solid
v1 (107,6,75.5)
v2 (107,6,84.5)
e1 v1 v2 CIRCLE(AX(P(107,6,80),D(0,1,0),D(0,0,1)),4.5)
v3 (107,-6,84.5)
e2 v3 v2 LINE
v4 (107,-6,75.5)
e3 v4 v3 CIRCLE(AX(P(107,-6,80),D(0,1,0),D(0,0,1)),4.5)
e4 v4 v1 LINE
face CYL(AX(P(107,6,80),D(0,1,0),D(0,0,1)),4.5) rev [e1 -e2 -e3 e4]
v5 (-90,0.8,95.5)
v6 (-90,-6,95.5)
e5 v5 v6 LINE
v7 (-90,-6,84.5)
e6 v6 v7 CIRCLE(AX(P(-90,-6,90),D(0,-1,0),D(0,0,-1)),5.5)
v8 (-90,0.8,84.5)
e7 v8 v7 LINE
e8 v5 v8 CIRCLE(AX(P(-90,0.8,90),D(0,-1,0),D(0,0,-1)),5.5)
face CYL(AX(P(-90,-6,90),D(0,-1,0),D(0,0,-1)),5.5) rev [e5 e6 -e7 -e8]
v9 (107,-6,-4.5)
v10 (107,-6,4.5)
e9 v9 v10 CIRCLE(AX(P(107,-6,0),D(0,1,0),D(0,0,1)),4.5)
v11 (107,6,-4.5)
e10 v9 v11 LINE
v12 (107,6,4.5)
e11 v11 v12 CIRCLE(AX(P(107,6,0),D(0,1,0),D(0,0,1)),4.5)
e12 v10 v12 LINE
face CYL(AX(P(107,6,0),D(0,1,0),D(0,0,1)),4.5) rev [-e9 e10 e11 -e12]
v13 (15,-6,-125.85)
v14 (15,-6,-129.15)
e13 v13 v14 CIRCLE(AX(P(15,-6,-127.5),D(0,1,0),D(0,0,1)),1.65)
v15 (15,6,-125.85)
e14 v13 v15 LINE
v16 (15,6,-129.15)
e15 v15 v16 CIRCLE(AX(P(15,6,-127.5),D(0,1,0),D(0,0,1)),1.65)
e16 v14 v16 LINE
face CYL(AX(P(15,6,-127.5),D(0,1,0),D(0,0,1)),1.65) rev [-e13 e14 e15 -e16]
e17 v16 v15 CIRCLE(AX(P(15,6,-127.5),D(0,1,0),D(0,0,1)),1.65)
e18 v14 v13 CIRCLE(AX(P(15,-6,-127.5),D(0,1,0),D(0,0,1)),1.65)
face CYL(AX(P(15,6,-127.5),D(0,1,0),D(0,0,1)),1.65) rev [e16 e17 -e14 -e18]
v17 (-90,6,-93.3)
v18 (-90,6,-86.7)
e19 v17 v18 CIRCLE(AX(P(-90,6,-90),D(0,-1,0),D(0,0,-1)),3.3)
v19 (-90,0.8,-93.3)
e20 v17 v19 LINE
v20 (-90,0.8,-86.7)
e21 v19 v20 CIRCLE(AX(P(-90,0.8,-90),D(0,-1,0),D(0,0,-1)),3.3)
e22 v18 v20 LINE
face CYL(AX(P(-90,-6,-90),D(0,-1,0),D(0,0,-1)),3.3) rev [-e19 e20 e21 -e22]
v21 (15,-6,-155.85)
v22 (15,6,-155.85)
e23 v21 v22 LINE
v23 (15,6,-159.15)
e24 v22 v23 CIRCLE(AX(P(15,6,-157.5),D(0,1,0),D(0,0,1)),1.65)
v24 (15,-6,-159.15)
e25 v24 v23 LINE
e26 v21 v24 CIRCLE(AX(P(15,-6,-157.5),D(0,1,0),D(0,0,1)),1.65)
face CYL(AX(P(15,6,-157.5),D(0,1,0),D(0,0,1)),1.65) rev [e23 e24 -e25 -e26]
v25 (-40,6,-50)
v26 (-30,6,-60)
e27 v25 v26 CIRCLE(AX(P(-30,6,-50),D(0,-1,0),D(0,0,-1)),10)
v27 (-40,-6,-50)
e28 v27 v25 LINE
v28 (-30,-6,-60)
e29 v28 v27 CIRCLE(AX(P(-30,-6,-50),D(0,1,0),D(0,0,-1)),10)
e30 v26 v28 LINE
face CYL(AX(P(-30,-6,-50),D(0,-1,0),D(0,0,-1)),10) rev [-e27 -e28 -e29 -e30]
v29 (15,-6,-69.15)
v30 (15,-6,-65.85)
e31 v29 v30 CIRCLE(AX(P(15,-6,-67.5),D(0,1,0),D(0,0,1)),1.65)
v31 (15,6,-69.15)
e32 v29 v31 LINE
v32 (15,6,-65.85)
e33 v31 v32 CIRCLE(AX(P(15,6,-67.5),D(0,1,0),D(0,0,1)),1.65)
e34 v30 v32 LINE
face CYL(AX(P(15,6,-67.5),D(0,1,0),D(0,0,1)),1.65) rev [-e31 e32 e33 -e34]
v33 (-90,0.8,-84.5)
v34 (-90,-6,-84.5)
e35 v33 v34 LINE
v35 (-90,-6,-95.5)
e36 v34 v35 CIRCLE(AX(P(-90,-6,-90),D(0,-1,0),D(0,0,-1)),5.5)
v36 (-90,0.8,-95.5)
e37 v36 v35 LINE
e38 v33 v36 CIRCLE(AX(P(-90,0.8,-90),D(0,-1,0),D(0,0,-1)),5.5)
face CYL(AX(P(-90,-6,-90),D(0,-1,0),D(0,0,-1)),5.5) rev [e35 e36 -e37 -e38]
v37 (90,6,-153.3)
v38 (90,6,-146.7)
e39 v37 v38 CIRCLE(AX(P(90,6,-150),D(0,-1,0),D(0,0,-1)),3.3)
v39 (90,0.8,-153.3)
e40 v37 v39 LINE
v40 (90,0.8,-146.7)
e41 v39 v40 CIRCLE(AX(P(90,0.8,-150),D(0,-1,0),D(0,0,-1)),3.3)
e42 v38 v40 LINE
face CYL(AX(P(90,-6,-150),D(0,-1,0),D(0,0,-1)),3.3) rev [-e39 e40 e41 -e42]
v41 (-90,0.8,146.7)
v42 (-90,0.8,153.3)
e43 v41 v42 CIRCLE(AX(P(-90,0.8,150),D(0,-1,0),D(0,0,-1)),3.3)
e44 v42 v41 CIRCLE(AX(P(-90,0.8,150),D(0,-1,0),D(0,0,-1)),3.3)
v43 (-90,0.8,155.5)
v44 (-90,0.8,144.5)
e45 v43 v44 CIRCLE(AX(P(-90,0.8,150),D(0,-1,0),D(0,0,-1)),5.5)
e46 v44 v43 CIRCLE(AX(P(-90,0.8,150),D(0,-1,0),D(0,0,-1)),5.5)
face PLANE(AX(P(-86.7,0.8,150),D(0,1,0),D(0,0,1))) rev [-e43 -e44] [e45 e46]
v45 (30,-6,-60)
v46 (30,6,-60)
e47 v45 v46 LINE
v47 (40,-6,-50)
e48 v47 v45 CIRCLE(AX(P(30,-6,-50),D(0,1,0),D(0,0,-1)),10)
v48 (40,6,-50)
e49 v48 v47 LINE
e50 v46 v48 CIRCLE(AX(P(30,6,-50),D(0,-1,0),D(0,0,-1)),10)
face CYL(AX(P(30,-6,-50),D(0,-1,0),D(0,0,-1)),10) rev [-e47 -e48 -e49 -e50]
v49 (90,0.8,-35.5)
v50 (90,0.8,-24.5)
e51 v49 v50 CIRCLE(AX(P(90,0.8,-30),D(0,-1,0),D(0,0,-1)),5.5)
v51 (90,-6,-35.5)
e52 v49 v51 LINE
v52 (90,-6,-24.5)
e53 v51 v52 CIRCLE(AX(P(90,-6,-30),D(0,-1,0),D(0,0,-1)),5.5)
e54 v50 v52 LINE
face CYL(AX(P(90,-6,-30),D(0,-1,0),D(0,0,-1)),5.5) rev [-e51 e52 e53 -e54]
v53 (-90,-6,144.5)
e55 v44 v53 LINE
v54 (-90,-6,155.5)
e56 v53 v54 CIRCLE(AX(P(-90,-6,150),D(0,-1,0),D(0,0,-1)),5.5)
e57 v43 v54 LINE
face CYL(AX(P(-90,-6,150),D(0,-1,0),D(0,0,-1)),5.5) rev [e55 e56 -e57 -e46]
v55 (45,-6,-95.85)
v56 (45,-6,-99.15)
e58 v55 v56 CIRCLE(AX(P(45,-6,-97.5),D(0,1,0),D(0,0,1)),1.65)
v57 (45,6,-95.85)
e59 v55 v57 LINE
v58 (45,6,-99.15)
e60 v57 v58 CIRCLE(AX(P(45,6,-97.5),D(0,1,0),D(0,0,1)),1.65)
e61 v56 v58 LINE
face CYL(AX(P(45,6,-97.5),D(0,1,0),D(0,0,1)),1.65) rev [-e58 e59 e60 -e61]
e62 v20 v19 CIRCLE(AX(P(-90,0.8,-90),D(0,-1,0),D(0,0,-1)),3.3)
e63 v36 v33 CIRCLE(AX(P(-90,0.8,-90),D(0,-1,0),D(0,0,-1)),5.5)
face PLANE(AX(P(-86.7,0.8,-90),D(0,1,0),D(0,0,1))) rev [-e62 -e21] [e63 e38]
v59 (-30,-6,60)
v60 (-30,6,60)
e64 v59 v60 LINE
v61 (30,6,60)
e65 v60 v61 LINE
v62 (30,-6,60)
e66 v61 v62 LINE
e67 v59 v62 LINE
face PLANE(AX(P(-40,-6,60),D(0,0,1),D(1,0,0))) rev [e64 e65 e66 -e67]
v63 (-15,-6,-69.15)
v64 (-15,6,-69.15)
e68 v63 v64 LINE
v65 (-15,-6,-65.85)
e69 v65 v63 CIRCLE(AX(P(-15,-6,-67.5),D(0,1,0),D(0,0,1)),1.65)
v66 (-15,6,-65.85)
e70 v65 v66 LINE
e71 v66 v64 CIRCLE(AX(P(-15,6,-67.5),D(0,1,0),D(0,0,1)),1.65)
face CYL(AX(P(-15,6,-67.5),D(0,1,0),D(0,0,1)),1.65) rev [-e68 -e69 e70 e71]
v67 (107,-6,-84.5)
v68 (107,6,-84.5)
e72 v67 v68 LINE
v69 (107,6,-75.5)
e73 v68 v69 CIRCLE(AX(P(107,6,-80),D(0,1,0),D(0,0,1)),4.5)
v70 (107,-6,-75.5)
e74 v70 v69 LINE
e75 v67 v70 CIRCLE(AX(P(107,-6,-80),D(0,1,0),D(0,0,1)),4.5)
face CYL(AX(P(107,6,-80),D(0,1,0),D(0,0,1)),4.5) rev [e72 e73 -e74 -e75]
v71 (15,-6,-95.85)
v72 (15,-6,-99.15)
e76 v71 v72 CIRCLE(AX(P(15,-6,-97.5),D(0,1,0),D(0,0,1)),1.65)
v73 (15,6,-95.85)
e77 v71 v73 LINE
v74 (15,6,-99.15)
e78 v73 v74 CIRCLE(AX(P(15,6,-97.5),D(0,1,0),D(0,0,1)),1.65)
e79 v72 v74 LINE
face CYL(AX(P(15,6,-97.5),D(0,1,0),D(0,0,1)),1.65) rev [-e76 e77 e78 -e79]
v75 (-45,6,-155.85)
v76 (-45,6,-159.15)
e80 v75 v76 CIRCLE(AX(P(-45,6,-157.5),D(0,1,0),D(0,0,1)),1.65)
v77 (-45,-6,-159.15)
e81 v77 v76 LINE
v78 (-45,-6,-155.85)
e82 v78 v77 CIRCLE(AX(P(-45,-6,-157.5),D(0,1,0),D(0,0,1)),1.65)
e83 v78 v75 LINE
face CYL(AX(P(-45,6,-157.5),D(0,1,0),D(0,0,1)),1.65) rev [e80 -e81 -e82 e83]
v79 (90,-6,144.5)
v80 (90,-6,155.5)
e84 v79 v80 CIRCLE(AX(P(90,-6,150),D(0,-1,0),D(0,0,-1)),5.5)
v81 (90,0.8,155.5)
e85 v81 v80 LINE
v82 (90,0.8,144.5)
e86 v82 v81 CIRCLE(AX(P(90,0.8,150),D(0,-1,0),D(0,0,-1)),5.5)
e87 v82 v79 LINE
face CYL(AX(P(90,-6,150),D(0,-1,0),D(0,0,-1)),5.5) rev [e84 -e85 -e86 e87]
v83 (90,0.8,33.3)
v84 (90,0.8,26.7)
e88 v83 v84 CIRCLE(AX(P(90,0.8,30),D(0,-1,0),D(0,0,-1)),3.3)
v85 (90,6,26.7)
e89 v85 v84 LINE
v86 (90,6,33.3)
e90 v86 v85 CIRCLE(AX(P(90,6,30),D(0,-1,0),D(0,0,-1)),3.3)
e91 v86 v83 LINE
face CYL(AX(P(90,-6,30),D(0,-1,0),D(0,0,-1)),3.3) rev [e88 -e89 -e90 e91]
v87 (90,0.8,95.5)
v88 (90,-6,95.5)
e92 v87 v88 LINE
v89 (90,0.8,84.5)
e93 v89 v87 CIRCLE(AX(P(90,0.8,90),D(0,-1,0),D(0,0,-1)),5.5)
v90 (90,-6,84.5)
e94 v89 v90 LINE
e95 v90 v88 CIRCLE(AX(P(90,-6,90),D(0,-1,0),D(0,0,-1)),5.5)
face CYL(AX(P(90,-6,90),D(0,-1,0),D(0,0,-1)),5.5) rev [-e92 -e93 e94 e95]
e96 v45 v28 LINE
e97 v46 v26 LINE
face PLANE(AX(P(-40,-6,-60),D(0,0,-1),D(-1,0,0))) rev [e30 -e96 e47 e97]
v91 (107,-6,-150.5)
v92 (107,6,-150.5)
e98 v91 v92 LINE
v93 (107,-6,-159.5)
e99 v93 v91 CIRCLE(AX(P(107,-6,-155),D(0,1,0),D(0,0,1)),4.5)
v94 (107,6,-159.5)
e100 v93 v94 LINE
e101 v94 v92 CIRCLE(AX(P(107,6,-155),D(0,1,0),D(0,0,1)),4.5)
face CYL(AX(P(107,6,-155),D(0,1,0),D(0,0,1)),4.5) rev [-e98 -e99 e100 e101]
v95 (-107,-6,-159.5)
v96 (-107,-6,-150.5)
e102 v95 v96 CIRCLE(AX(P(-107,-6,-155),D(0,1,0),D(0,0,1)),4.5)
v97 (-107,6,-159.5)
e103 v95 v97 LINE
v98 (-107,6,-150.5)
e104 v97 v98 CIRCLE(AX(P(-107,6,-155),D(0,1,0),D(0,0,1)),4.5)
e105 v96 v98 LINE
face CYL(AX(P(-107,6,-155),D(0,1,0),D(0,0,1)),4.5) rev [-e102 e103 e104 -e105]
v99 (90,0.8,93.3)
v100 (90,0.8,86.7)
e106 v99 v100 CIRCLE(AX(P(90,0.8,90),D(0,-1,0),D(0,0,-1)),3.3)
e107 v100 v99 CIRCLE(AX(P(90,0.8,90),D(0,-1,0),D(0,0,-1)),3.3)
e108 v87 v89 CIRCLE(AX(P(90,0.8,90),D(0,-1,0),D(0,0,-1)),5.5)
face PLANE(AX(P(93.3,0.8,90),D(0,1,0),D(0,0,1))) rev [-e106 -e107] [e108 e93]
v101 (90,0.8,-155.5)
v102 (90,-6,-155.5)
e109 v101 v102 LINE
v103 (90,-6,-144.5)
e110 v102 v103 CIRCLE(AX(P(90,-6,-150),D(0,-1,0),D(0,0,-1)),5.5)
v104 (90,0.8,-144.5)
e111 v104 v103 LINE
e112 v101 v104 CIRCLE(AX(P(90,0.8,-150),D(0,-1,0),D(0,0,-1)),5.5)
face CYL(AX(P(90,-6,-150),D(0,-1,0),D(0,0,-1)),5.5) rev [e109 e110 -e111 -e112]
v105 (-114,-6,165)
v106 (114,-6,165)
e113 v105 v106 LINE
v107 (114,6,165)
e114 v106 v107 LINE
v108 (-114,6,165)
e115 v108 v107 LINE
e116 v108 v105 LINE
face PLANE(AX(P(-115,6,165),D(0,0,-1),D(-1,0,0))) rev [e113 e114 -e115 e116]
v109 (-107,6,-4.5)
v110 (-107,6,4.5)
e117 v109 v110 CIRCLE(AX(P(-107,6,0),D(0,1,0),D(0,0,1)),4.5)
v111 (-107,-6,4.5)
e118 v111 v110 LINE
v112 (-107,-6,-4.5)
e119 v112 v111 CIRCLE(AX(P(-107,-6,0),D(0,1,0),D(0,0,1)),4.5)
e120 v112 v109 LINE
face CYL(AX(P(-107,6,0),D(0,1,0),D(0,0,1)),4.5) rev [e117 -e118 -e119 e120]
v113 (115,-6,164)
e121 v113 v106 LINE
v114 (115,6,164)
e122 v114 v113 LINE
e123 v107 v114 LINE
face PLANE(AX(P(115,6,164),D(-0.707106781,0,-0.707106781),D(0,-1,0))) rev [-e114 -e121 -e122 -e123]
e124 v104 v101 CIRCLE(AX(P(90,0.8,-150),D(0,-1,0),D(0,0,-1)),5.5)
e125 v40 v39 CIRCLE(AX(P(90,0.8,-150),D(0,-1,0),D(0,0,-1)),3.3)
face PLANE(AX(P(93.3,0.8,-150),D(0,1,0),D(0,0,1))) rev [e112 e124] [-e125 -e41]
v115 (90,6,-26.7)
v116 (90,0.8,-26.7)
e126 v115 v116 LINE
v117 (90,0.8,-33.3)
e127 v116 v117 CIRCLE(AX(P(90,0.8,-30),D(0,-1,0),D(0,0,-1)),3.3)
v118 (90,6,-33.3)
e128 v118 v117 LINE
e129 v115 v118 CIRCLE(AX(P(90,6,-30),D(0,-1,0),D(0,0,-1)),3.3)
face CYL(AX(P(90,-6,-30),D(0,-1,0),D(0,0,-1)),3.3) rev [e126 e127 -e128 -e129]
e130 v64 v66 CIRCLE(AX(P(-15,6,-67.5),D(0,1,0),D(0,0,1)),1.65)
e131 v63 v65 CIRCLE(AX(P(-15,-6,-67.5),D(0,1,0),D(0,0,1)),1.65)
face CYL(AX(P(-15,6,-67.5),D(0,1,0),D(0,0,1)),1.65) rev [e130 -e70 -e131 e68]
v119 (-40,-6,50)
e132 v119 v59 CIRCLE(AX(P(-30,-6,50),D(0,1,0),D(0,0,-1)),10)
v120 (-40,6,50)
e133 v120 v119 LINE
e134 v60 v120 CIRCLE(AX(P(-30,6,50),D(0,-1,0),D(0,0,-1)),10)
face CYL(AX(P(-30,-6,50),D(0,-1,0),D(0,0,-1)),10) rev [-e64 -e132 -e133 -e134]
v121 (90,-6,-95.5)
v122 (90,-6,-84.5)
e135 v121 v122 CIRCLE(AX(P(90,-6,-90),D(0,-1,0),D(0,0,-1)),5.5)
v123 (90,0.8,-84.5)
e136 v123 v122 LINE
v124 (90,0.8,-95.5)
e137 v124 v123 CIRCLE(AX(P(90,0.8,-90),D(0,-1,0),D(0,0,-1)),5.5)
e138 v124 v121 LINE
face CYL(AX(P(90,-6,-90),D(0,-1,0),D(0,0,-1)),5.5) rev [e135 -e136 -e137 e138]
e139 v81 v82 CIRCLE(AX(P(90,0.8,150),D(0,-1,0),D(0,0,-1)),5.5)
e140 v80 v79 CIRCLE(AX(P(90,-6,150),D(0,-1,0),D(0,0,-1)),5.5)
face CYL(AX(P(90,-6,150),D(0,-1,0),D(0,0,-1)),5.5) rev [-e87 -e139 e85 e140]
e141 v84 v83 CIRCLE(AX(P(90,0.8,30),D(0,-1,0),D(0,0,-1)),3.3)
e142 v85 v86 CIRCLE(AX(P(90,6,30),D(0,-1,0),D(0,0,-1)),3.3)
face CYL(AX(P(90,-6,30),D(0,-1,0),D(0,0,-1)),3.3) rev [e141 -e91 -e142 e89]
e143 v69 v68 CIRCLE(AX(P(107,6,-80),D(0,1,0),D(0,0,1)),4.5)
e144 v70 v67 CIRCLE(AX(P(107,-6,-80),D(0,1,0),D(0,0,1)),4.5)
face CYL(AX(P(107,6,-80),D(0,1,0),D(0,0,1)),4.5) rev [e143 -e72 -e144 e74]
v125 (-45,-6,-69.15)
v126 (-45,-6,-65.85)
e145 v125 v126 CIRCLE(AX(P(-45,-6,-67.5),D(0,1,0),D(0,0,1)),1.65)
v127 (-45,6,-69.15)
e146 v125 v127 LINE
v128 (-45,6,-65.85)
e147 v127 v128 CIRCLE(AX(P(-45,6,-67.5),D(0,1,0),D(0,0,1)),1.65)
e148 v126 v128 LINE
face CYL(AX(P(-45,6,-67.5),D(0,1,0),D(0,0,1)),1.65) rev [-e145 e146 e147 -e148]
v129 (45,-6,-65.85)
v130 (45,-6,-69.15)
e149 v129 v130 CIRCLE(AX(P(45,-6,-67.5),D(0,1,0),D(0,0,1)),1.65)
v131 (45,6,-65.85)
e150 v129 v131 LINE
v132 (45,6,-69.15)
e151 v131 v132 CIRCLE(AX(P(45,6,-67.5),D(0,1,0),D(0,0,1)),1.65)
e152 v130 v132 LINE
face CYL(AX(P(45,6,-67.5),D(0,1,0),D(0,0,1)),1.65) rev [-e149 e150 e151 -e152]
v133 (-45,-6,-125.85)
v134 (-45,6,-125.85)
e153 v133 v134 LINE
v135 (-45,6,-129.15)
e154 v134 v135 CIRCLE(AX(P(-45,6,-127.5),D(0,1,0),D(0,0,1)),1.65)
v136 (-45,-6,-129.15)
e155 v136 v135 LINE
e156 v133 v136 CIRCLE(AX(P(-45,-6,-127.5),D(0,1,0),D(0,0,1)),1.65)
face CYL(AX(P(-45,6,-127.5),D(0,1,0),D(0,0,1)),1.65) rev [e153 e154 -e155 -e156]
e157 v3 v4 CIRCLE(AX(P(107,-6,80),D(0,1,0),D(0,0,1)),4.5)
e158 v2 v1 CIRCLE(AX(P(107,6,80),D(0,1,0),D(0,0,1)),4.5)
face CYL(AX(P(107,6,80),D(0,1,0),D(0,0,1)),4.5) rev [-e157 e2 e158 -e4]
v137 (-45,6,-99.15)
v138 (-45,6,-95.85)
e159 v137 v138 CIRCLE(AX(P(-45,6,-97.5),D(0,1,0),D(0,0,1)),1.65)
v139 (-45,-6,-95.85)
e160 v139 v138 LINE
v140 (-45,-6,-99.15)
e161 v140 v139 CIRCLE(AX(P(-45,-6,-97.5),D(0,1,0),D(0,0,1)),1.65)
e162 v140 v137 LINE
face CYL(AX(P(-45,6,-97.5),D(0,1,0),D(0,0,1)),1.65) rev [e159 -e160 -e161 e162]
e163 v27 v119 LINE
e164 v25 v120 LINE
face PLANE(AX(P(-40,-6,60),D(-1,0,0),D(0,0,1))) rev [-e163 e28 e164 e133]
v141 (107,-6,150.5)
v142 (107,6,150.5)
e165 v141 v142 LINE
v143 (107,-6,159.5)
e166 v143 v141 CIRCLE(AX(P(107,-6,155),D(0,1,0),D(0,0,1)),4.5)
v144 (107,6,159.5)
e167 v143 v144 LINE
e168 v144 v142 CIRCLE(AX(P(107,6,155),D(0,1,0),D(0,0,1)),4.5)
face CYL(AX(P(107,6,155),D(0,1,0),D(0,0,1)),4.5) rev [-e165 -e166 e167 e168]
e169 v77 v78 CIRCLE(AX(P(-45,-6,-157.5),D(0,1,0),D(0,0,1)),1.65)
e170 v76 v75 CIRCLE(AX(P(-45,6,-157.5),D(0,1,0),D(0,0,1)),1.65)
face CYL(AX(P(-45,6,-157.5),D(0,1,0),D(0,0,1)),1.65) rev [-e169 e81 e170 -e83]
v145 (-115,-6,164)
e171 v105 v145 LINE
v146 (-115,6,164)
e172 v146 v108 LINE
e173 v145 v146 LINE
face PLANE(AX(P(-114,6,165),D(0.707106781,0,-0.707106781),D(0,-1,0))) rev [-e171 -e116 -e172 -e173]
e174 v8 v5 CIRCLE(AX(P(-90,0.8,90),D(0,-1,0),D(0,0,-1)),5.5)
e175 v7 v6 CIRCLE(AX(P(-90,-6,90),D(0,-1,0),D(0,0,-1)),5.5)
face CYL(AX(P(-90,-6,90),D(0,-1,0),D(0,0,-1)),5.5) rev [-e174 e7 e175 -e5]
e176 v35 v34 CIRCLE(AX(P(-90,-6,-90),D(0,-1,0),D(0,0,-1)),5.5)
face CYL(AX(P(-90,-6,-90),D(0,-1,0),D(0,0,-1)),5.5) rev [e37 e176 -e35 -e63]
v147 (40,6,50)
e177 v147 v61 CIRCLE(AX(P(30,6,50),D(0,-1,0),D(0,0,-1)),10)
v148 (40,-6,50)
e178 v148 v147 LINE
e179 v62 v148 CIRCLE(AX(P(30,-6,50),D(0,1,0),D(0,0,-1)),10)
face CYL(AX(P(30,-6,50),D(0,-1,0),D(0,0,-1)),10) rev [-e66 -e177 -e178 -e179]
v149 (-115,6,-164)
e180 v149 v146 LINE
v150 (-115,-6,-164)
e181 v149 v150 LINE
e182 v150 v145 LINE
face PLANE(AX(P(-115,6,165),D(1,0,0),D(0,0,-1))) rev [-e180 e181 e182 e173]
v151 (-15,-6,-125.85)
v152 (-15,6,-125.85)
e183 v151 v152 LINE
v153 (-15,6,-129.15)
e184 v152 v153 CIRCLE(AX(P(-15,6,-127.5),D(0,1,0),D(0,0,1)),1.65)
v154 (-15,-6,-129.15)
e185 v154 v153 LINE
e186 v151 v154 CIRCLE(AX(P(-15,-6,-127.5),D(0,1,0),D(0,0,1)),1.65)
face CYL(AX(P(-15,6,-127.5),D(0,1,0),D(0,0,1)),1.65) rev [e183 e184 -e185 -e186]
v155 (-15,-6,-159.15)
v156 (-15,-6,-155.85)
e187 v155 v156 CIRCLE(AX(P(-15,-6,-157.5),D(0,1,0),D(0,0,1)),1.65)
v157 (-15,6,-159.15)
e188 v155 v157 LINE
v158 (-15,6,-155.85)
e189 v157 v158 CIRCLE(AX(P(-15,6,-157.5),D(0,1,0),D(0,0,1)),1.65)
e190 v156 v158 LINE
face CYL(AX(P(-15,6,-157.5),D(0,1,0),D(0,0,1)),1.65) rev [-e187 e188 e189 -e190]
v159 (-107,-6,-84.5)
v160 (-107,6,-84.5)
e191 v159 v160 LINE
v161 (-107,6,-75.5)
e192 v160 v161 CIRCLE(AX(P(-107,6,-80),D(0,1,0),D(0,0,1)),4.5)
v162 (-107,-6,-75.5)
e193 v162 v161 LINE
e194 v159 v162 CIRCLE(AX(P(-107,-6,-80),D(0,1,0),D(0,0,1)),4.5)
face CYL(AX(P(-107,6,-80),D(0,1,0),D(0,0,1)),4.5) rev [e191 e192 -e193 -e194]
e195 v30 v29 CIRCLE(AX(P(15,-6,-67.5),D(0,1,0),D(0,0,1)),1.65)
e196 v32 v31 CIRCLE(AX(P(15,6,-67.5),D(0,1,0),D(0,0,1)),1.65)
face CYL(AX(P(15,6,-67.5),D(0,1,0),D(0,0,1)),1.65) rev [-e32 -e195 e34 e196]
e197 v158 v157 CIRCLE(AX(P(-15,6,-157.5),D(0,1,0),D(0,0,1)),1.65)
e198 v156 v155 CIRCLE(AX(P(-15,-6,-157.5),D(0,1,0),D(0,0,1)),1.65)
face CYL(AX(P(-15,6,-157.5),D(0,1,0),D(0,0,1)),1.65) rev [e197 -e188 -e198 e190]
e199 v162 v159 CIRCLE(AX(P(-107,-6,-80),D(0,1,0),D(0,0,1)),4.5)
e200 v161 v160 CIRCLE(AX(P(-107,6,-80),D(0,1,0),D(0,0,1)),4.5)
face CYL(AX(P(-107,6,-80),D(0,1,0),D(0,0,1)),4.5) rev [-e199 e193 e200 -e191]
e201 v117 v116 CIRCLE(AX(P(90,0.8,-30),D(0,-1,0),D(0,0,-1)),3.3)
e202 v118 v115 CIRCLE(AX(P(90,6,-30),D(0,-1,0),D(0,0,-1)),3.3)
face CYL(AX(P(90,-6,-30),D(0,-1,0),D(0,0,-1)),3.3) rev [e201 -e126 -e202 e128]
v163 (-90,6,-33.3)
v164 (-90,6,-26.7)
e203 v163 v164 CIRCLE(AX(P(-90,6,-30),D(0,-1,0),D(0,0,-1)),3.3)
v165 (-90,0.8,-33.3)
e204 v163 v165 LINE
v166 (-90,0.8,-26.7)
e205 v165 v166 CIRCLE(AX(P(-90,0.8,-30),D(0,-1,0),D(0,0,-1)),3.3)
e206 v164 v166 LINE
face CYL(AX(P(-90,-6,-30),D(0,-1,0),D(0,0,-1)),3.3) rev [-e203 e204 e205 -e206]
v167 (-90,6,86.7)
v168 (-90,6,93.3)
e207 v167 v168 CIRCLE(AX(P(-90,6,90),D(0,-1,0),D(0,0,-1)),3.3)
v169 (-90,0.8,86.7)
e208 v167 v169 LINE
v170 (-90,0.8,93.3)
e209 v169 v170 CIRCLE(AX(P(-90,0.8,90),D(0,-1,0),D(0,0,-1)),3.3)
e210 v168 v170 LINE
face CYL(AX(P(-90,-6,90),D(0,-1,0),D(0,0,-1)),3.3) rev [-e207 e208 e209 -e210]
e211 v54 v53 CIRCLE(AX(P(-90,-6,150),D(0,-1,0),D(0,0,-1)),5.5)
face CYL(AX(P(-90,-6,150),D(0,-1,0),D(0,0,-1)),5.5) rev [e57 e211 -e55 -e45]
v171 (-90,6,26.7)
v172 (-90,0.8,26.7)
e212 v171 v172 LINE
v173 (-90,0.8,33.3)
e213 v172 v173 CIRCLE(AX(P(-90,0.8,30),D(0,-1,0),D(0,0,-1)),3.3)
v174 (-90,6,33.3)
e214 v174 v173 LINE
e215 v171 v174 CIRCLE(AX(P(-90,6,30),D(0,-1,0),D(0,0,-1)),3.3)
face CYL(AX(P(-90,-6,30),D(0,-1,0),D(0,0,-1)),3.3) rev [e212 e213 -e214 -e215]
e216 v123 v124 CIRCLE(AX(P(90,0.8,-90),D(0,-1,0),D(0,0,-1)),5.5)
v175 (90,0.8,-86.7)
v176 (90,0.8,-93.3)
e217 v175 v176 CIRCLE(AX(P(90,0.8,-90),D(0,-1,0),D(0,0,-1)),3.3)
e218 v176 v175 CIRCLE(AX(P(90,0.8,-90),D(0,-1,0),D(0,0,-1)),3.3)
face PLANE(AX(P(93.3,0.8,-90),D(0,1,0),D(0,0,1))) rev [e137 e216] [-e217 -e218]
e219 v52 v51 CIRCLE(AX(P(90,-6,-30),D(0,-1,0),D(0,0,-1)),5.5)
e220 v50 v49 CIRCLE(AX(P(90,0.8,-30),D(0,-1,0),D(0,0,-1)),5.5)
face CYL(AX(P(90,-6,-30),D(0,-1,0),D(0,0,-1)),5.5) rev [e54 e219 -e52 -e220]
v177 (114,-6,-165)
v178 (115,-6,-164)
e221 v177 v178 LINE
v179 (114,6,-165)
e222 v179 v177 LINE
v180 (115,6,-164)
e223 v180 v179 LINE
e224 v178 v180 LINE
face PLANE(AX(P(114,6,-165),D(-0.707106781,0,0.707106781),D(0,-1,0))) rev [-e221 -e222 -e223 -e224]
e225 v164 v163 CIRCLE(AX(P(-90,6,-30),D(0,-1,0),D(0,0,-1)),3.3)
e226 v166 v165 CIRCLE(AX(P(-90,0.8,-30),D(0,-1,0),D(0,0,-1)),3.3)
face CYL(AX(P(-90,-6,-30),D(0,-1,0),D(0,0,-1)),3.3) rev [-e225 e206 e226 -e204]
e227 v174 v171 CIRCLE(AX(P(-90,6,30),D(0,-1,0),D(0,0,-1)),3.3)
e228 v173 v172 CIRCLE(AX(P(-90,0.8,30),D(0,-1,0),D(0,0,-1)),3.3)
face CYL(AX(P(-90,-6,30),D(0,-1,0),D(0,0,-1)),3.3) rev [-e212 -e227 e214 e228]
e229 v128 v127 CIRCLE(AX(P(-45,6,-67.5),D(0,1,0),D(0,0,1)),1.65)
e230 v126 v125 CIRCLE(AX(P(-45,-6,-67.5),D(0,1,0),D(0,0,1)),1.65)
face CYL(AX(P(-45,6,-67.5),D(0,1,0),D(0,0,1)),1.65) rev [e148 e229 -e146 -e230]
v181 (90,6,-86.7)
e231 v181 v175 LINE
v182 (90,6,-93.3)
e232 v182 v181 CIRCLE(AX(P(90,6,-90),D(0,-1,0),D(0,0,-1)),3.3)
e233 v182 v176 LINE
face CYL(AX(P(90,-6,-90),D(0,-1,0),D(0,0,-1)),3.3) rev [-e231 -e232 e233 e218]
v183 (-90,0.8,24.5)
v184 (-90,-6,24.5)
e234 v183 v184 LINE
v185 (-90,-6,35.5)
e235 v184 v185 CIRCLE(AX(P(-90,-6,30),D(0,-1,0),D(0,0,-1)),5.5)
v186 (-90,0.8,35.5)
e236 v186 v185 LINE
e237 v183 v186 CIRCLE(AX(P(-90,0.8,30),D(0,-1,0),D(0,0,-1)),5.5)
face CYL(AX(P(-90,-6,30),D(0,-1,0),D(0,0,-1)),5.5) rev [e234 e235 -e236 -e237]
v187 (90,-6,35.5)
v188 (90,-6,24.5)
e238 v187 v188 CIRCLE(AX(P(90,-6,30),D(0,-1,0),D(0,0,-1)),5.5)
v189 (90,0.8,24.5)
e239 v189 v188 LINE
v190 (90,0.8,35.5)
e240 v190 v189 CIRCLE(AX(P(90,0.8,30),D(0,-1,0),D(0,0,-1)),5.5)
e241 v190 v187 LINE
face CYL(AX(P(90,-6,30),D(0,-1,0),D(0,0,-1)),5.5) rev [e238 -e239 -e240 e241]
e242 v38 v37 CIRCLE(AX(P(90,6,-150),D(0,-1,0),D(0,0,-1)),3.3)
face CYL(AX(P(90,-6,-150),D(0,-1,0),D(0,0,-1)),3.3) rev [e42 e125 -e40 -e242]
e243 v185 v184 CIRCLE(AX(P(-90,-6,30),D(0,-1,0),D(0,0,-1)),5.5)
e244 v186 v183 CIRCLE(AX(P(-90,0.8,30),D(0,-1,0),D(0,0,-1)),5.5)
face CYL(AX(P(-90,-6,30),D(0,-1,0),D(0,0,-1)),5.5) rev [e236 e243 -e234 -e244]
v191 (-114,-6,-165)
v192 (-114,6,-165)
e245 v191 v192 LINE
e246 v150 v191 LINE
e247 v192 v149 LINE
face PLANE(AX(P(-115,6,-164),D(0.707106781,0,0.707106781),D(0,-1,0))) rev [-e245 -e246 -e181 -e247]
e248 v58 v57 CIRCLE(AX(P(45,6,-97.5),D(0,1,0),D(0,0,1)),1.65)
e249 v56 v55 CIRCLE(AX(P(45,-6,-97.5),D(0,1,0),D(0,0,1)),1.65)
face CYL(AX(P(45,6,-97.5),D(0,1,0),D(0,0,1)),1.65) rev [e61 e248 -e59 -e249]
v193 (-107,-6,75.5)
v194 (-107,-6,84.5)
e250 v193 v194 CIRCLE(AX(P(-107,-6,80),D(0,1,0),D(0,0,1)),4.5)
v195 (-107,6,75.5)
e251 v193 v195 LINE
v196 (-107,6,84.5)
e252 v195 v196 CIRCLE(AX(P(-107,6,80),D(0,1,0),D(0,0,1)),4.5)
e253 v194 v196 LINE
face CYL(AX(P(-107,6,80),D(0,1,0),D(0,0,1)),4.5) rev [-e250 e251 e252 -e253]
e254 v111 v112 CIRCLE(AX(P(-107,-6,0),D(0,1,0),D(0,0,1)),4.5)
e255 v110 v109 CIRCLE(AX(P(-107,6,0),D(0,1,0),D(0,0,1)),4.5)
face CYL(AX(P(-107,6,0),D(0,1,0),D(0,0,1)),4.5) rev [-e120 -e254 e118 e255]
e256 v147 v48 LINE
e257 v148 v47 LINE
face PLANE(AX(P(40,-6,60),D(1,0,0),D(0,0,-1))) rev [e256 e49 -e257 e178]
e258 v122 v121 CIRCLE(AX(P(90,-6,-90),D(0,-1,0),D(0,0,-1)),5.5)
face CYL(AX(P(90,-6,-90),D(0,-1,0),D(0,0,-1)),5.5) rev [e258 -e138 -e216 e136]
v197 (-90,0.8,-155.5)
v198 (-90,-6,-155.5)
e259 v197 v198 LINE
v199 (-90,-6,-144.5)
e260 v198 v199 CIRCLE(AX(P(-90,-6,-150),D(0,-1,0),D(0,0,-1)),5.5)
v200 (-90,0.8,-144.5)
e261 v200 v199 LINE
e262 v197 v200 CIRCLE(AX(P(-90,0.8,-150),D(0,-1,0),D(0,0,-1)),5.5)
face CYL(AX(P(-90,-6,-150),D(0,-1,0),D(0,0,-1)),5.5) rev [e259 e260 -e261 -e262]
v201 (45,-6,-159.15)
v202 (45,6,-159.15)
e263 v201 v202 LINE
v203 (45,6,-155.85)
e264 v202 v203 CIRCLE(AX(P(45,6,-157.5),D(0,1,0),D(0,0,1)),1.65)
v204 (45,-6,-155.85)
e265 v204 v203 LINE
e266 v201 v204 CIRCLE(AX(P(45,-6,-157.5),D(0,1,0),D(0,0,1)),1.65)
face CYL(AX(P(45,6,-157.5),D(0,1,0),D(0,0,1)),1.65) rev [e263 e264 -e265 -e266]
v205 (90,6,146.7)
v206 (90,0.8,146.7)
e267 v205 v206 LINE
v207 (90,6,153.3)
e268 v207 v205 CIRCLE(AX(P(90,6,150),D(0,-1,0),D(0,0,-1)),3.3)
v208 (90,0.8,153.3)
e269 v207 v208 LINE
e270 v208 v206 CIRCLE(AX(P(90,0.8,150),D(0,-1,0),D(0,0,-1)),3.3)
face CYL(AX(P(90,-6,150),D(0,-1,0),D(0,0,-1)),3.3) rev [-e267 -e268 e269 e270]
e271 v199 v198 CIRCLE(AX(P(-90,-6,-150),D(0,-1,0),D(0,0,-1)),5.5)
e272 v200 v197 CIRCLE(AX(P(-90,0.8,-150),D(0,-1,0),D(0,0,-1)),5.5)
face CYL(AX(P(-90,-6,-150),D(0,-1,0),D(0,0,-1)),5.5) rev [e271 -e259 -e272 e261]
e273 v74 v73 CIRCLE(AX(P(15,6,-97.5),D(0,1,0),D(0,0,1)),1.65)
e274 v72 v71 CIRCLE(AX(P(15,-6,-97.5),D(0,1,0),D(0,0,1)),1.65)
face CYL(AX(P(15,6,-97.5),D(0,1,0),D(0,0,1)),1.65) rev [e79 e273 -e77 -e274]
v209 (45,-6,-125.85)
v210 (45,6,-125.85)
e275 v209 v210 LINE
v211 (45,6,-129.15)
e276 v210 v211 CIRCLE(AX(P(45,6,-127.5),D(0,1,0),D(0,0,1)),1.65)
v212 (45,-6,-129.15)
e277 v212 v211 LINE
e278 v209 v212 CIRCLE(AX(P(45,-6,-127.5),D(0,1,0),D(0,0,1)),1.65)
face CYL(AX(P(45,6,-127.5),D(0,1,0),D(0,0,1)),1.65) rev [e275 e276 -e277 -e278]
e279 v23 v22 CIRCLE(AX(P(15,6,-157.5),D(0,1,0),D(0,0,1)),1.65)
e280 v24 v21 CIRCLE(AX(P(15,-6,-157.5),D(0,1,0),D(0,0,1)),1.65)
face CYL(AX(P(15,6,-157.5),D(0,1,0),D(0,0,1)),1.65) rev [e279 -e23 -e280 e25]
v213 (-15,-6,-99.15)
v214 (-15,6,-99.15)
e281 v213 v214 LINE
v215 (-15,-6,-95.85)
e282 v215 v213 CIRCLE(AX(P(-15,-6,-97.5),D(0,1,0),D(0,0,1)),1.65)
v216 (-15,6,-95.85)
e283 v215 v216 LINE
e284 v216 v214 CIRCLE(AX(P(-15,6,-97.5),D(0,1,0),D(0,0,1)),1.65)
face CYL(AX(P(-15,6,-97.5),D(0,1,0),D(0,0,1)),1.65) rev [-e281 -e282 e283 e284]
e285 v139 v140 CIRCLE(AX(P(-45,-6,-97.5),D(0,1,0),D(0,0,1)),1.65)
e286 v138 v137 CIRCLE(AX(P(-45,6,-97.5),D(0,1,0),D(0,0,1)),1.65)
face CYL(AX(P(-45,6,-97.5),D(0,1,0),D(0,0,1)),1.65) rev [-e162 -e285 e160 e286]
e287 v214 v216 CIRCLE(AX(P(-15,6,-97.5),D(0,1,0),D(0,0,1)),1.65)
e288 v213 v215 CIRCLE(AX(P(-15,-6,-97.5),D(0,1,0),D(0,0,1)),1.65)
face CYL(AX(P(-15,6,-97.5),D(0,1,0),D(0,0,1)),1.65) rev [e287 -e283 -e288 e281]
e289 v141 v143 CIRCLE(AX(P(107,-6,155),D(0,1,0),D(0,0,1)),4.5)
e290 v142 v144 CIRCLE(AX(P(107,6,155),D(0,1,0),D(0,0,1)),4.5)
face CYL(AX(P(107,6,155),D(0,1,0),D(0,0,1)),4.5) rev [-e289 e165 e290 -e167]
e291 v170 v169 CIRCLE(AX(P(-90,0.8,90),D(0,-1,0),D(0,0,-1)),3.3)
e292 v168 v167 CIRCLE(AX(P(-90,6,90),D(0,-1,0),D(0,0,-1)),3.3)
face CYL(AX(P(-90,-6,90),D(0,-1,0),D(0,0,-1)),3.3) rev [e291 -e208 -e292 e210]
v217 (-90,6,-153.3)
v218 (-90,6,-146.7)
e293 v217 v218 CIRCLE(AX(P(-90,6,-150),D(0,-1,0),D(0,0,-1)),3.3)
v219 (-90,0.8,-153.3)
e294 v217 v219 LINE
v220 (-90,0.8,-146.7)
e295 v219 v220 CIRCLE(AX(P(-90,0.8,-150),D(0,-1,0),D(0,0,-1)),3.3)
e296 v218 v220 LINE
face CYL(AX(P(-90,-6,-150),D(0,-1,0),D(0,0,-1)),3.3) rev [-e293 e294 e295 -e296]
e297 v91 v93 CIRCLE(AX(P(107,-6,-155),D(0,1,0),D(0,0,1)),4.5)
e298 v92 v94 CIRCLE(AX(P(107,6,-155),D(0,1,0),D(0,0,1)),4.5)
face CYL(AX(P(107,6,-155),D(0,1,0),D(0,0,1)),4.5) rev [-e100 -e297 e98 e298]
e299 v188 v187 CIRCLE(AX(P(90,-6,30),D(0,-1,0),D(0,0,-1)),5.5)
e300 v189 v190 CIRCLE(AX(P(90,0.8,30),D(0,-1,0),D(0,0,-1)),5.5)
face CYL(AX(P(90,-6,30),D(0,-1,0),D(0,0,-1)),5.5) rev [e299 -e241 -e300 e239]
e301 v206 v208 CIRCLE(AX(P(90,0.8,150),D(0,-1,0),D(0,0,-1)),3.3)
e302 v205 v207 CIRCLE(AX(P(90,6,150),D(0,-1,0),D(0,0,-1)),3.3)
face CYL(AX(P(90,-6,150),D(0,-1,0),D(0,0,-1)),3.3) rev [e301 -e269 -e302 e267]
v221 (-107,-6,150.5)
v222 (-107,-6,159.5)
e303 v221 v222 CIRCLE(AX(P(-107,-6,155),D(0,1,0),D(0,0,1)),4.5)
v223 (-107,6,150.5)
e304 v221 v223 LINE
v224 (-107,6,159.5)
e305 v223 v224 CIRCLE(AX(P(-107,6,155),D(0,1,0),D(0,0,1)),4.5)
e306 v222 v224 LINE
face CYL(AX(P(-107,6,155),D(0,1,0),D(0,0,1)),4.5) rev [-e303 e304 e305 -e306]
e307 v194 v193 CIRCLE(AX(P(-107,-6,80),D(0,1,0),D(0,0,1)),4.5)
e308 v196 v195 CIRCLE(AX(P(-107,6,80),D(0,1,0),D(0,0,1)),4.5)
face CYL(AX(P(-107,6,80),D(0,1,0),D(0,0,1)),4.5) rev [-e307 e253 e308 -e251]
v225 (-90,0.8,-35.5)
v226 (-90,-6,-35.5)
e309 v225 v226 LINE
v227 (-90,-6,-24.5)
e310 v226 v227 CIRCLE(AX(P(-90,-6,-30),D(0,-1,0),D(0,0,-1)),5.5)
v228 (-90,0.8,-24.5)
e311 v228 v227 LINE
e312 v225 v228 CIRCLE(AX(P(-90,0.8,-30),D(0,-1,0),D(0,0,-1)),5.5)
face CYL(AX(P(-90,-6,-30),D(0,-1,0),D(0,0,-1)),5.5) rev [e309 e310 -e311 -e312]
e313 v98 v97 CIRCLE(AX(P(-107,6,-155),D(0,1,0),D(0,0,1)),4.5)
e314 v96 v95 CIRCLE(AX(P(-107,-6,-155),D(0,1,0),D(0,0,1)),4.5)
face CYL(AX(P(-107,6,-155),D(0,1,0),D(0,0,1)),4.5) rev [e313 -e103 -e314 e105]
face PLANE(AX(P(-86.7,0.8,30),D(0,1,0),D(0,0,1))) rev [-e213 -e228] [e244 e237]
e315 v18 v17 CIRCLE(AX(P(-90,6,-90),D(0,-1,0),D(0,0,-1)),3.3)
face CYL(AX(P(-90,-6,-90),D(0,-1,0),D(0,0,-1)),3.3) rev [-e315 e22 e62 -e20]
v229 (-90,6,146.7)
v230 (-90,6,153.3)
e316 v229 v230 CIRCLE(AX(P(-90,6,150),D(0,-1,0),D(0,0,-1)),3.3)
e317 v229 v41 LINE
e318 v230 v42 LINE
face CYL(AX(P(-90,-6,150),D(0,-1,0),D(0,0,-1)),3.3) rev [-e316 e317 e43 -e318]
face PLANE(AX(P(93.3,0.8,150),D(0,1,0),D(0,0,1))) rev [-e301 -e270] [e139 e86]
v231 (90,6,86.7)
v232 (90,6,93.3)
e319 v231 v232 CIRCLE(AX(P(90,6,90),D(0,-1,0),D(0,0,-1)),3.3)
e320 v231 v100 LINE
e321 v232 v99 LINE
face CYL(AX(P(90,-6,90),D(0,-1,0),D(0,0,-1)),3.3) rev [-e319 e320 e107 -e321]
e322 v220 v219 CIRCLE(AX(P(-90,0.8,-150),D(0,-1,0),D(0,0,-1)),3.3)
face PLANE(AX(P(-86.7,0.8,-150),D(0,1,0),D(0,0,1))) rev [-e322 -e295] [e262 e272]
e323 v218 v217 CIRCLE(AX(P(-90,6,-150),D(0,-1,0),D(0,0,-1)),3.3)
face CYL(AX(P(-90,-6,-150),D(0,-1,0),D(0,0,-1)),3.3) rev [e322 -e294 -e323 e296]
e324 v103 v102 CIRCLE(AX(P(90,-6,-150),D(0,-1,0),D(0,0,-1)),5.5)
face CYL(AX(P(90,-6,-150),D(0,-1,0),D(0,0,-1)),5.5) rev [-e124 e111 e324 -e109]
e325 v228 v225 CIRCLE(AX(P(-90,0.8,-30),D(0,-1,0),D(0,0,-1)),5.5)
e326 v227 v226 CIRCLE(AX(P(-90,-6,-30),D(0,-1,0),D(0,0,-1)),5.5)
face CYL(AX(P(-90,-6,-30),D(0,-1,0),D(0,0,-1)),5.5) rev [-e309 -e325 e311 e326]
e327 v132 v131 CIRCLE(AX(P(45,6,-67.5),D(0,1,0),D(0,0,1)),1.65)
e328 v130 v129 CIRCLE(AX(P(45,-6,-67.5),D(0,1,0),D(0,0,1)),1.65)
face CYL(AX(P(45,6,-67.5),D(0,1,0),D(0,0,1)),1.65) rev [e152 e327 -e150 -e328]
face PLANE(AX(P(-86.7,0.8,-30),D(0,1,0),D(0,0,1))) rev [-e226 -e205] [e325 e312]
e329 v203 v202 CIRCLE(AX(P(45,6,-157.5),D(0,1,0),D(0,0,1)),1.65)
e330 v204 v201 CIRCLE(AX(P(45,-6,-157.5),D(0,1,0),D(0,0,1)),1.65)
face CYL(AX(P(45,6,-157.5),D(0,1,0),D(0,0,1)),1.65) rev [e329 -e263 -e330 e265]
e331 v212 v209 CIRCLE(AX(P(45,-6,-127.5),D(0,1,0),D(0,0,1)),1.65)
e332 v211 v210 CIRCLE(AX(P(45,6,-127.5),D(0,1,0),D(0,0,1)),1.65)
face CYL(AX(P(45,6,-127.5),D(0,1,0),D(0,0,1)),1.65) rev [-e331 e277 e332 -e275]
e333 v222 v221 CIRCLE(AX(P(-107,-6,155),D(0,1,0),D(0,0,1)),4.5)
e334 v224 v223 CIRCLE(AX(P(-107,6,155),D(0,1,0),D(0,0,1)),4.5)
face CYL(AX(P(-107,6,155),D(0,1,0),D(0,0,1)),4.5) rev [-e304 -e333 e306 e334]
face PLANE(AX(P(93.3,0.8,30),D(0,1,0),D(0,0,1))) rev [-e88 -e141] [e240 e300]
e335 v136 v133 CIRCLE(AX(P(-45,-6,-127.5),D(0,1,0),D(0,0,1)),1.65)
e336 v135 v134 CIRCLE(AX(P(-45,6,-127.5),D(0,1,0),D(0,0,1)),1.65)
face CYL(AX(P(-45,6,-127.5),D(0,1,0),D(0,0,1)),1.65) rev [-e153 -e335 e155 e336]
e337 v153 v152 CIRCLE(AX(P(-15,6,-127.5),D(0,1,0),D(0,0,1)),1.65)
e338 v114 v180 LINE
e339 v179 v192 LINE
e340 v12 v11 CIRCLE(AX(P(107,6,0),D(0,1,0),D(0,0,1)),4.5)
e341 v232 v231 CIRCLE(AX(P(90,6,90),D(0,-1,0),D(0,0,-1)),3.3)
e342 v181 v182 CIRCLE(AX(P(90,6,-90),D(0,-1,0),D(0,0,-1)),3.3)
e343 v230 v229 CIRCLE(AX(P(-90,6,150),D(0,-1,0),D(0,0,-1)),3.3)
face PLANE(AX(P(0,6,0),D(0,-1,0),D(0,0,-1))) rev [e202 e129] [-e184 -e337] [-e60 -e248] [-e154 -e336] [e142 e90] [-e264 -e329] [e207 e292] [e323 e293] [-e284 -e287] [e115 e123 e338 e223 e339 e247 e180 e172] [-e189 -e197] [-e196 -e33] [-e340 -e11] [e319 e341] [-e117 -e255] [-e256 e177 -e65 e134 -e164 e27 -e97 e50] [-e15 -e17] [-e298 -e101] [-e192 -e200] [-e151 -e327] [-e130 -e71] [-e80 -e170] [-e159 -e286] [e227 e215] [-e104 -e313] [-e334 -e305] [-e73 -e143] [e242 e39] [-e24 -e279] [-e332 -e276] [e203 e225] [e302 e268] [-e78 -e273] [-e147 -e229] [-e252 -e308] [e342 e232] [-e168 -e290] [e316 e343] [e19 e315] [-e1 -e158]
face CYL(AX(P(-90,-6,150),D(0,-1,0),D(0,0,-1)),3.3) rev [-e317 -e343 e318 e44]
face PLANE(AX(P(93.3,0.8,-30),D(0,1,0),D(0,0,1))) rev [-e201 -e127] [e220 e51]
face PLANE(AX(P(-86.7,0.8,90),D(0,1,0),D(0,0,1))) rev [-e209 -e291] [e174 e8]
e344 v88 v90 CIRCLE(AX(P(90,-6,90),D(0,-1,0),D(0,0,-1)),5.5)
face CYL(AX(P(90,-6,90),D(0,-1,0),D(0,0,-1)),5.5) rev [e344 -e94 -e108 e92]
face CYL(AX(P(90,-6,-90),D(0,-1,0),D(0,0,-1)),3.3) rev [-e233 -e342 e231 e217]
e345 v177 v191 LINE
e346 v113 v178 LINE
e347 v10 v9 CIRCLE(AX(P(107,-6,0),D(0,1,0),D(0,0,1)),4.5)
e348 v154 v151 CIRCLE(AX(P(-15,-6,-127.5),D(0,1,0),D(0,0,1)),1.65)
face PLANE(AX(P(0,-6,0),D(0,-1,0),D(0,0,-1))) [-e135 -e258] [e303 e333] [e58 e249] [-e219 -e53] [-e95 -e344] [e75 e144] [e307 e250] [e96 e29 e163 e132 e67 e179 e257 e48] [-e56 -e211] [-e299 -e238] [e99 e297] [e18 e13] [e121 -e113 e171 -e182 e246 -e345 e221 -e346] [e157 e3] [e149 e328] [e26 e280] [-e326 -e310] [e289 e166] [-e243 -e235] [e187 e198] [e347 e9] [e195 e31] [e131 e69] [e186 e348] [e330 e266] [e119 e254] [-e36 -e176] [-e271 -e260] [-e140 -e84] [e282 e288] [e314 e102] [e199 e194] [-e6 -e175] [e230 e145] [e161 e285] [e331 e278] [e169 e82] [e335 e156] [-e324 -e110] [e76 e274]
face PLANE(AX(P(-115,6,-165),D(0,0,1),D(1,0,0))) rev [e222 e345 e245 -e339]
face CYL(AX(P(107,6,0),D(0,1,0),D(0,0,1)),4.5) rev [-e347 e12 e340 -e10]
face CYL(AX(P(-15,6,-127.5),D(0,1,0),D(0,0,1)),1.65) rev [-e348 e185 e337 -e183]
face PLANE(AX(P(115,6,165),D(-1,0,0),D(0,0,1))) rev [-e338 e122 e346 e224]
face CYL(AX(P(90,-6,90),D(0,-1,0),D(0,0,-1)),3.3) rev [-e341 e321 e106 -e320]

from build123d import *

# Parameters (mm, degrees)
SKETCH_1_W                = 230
SKETCH_1_H                = 330
EXTRUDE_1_DEPTH           = 6
HOLE_WIZARD_M8_1_D        = 9
CHAMFER_1_SIZE            = 1
HOLE_WIZARD_1_D           = 6.6
HOLE_WIZARD_1_CBORE_D     = 11
HOLE_WIZARD_1_CBORE_DEPTH = 6.8
SKETCH_6_W                = 80
SKETCH_6_H                = 120
CUT_EXTRUDE_1_DEPTH       = 202.479527496
FILLET_1_R                = 10
HOLE_WIZARD_M4_1_D        = 3.3


with BuildPart() as part:
    # 草图1 → 凸台-拉伸1 (new, symmetric)
    with BuildSketch(Plane(origin=(0, 0, 0), x_dir=(1, 0, 0), z_dir=(0, 1, 0))):
        Rectangle(SKETCH_1_W, SKETCH_1_H)
    extrude(amount=EXTRUDE_1_DEPTH, both=True)

    # M8 间隙孔1 (through all)
    with Locations(Plane(origin=(0, 6, 0), x_dir=(1, 0, 0), z_dir=(0, 1, 0))):
        with Locations((-107, 155), (-107, 80), (107, 80), (107, 155), (-107, 0), (-107, -155), (-107, -80), (107, -80), (107, -155), (107, 0)):
            Hole(HOLE_WIZARD_M8_1_D / 2)

    # 倒角1
    chamfer_1_edges = [part.edges().sort_by_distance(p)[0] for p in [
        (115, 0, 165),
        (-115, 0, 165),
        (-115, 0, -165),
        (115, 0, -165),
    ]]
    chamfer(chamfer_1_edges, length=CHAMFER_1_SIZE)

    # 打孔尺寸(%根据)内六角圆柱头螺钉的类型1 (through all)
    with Locations(Plane(origin=(0, -6, 0), x_dir=(-1, 0, 0), z_dir=(0, -1, 0))):
        with Locations((90, -150), (-90, -150), (90, -90), (-90, -90), (90, -30), (-90, -30), (90, 30), (-90, 30), (90, 90), (-90, 90), (90, 150), (-90, 150)):
            CounterBoreHole(HOLE_WIZARD_1_D / 2, HOLE_WIZARD_1_CBORE_D / 2, HOLE_WIZARD_1_CBORE_DEPTH)

    # 草图6 → 切除-拉伸1 (cut, through all)
    with BuildSketch(Plane(origin=(0, 6, 0), x_dir=(1, 0, 0), z_dir=(0, 1, 0))):
        Rectangle(SKETCH_6_W, SKETCH_6_H)
    extrude(amount=-CUT_EXTRUDE_1_DEPTH, mode=Mode.SUBTRACT)

    # 圆角1
    fillet_1_edges = [part.edges().sort_by_distance(p)[0] for p in [
        (40, 0, -60),
        (40, 0, 60),
        (-40, 0, 60),
        (-40, 0, -60),
    ]]
    fillet(fillet_1_edges, radius=FILLET_1_R)

    # M4 螺纹孔1 (through all)
    with Locations(Plane(origin=(0, 6, 0), x_dir=(1, 0, 0), z_dir=(0, 1, 0))):
        with Locations((-45, 67.5), (-45, 157.5), (-15, 157.5), (15, 157.5), (45, 157.5), (-15, 127.5), (15, 127.5), (45, 127.5), (-15, 97.5), (15, 97.5), (45, 97.5), (-15, 67.5), (15, 67.5), (45, 67.5), (-45, 127.5), (-45, 97.5)):
            Hole(HOLE_WIZARD_M4_1_D / 2)


solid = part.part
